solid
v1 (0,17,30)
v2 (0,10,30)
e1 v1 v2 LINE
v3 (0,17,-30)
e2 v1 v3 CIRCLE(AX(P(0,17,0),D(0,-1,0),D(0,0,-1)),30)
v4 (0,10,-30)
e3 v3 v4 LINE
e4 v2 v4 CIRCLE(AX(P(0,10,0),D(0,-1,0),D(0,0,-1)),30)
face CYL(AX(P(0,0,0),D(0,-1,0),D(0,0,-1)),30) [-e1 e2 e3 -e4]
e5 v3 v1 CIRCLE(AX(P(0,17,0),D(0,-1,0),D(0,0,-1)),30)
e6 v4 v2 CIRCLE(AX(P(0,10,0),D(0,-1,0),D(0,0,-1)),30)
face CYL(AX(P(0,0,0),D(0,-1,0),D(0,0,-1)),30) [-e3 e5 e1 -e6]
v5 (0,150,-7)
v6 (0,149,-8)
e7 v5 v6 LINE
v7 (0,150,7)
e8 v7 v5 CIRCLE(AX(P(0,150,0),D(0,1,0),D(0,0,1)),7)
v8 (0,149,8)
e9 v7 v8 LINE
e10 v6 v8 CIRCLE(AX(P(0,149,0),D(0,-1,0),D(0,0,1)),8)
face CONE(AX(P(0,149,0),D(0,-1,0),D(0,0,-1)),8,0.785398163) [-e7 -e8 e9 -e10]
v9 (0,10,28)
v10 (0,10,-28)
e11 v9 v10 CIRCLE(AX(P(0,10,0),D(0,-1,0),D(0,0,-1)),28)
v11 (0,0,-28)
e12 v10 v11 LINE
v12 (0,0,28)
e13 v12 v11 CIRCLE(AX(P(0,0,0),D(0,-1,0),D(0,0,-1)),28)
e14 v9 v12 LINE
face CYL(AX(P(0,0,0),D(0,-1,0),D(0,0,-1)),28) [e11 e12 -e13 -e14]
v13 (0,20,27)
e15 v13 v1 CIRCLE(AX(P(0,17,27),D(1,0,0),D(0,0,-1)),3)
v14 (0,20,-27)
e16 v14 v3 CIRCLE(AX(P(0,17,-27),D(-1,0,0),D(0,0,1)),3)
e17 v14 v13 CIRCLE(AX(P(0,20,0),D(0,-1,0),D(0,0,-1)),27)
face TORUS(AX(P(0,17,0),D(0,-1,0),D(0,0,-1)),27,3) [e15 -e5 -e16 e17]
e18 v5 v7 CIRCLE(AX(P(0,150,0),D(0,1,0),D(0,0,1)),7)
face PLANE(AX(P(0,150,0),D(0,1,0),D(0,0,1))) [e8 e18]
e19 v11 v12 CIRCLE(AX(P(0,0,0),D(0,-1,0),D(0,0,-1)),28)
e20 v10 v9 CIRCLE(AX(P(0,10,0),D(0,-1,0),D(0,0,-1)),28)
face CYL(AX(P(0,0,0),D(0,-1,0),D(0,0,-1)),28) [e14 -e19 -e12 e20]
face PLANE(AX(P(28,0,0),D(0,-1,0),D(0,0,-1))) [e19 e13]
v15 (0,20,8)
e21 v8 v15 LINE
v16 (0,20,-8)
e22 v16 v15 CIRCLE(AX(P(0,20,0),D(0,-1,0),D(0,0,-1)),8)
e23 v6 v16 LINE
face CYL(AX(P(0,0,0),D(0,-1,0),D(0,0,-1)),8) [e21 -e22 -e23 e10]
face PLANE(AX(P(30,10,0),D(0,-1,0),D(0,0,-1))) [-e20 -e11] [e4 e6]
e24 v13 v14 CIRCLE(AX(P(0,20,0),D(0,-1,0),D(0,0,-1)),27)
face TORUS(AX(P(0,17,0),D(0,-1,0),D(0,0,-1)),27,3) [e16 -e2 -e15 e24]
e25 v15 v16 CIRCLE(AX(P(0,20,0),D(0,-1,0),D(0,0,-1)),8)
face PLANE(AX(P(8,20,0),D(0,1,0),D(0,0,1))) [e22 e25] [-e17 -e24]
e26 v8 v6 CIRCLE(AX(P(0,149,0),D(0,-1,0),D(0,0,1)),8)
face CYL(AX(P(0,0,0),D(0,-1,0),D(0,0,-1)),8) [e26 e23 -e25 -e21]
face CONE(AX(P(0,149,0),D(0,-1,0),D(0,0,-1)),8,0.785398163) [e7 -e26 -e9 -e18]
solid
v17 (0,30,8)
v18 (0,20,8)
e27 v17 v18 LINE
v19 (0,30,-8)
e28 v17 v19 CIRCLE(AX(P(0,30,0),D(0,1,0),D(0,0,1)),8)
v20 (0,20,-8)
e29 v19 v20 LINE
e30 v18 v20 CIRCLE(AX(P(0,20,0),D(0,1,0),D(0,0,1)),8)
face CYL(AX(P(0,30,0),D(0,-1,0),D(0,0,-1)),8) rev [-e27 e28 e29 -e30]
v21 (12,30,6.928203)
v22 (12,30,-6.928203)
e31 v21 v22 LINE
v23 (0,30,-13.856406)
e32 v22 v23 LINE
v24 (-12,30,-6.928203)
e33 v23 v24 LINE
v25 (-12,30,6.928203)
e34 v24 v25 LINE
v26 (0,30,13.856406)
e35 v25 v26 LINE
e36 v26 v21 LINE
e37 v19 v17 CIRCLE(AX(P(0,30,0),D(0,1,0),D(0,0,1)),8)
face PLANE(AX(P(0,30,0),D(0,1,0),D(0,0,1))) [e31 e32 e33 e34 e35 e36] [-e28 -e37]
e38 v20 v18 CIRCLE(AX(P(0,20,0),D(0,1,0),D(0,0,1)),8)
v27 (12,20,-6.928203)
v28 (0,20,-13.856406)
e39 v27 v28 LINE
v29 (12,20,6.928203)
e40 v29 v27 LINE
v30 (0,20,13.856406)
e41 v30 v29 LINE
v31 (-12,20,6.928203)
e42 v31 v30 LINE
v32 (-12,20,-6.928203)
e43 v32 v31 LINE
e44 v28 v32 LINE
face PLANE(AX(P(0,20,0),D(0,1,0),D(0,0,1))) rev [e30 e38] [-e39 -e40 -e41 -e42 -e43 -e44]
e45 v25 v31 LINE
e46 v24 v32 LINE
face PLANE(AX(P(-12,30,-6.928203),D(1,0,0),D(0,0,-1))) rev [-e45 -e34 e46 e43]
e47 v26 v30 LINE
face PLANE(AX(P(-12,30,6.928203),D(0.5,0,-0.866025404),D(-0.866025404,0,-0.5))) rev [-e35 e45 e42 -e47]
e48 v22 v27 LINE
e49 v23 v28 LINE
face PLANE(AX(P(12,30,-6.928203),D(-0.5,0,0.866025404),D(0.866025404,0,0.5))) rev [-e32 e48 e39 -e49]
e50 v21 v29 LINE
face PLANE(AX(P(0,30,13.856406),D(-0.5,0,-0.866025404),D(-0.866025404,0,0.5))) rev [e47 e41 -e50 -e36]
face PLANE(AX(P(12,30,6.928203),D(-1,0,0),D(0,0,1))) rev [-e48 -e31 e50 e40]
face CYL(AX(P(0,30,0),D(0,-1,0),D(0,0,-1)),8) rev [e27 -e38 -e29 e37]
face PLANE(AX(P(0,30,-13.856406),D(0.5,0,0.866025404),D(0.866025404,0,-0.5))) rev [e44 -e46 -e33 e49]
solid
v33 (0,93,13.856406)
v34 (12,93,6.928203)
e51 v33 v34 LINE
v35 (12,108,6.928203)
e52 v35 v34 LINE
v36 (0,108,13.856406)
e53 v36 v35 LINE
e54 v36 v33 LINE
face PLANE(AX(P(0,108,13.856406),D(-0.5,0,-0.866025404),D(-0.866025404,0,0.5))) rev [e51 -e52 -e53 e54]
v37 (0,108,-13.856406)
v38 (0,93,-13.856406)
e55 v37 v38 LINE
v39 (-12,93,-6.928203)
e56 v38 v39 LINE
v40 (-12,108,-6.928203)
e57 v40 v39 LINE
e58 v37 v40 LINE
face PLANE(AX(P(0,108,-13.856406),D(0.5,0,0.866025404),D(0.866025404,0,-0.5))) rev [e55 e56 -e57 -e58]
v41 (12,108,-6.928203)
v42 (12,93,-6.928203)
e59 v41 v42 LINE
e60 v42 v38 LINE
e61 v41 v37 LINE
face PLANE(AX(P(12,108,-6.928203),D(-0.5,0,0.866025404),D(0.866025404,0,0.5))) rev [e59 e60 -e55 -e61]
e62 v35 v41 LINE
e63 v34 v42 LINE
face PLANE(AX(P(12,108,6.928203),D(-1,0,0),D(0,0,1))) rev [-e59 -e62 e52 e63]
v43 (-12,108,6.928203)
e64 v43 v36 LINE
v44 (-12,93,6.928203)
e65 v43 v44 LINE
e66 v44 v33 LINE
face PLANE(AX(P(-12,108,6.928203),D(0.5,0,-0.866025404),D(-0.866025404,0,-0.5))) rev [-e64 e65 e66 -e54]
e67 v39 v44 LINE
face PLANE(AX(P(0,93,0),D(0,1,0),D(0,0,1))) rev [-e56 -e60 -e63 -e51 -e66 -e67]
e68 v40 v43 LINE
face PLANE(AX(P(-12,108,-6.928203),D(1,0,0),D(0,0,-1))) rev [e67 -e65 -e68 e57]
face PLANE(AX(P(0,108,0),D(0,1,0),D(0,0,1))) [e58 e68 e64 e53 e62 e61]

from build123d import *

# Parameters (mm, degrees)
SKETCH_2_R      = 8
EXTRUDE_1_DEPTH = 10
EXTRUDE_START   = 63
EXTRUDE_2_DEPTH = 15
CHAMFER_1_SIZE  = 1


with BuildPart() as part:
    # 草图1 → 旋转1 (revolve)
    with BuildSketch(Plane.XY, mode=Mode.PRIVATE) as revolve_1_sk:
        with BuildLine():
            Line((0, 0), (0, 150))
            Line((0, 150), (8, 150))
            Line((8, 150), (8, 20))
            Line((8, 20), (27, 20))
            ThreePointArc((27, 20), (29.121320344, 19.121320344), (30, 17))
            Line((30, 17), (30, 10))
            Line((30, 10), (28, 10))
            Line((28, 10), (28, 0))
            Line((28, 0), (0, 0))
        make_face()
    revolve(revolve_1_sk.sketch.rotate(Axis((0, 0, 0), (0, 1, 0)), 90), axis=Axis((0, 0, 0), (0, 1, 0)))

    # 倒角1
    chamfer_1_edges = [part.edges().sort_by_distance(p)[0] for p in [
        (0, 150, 8),
    ]]
    chamfer(chamfer_1_edges, length=CHAMFER_1_SIZE)


with BuildPart() as body_2:
    # 草图2 → 凸台-拉伸1 (new body)
    with BuildSketch(Plane(origin=(0, 20, 0), x_dir=(1, 0, 0), z_dir=(0, 1, 0))):
        Polygon((0, 13.856406461), (-12, 6.92820323), (-12, -6.92820323), (0, -13.856406461), (12, -6.92820323), (12, 6.92820323), align=None)
        with Locations(Location((0, 0, 0), (0, 0, 270))):
            Circle(SKETCH_2_R, mode=Mode.SUBTRACT)
    extrude(amount=EXTRUDE_1_DEPTH)


with BuildPart() as body_3:
    # 草图4 → 凸台-拉伸2 (new body)
    with BuildSketch(Plane(origin=(0, 30, 0), x_dir=(1, 0, 0), z_dir=(0, 1, 0)).offset(EXTRUDE_START)):
        Polygon((12, 6.92820323), (0, 13.856406461), (-12, 6.92820323), (-12, -6.92820323), (0, -13.856406461), (12, -6.92820323), align=None)
    extrude(amount=EXTRUDE_2_DEPTH)


solid = Compound([part.part, body_2.part, body_3.part])
